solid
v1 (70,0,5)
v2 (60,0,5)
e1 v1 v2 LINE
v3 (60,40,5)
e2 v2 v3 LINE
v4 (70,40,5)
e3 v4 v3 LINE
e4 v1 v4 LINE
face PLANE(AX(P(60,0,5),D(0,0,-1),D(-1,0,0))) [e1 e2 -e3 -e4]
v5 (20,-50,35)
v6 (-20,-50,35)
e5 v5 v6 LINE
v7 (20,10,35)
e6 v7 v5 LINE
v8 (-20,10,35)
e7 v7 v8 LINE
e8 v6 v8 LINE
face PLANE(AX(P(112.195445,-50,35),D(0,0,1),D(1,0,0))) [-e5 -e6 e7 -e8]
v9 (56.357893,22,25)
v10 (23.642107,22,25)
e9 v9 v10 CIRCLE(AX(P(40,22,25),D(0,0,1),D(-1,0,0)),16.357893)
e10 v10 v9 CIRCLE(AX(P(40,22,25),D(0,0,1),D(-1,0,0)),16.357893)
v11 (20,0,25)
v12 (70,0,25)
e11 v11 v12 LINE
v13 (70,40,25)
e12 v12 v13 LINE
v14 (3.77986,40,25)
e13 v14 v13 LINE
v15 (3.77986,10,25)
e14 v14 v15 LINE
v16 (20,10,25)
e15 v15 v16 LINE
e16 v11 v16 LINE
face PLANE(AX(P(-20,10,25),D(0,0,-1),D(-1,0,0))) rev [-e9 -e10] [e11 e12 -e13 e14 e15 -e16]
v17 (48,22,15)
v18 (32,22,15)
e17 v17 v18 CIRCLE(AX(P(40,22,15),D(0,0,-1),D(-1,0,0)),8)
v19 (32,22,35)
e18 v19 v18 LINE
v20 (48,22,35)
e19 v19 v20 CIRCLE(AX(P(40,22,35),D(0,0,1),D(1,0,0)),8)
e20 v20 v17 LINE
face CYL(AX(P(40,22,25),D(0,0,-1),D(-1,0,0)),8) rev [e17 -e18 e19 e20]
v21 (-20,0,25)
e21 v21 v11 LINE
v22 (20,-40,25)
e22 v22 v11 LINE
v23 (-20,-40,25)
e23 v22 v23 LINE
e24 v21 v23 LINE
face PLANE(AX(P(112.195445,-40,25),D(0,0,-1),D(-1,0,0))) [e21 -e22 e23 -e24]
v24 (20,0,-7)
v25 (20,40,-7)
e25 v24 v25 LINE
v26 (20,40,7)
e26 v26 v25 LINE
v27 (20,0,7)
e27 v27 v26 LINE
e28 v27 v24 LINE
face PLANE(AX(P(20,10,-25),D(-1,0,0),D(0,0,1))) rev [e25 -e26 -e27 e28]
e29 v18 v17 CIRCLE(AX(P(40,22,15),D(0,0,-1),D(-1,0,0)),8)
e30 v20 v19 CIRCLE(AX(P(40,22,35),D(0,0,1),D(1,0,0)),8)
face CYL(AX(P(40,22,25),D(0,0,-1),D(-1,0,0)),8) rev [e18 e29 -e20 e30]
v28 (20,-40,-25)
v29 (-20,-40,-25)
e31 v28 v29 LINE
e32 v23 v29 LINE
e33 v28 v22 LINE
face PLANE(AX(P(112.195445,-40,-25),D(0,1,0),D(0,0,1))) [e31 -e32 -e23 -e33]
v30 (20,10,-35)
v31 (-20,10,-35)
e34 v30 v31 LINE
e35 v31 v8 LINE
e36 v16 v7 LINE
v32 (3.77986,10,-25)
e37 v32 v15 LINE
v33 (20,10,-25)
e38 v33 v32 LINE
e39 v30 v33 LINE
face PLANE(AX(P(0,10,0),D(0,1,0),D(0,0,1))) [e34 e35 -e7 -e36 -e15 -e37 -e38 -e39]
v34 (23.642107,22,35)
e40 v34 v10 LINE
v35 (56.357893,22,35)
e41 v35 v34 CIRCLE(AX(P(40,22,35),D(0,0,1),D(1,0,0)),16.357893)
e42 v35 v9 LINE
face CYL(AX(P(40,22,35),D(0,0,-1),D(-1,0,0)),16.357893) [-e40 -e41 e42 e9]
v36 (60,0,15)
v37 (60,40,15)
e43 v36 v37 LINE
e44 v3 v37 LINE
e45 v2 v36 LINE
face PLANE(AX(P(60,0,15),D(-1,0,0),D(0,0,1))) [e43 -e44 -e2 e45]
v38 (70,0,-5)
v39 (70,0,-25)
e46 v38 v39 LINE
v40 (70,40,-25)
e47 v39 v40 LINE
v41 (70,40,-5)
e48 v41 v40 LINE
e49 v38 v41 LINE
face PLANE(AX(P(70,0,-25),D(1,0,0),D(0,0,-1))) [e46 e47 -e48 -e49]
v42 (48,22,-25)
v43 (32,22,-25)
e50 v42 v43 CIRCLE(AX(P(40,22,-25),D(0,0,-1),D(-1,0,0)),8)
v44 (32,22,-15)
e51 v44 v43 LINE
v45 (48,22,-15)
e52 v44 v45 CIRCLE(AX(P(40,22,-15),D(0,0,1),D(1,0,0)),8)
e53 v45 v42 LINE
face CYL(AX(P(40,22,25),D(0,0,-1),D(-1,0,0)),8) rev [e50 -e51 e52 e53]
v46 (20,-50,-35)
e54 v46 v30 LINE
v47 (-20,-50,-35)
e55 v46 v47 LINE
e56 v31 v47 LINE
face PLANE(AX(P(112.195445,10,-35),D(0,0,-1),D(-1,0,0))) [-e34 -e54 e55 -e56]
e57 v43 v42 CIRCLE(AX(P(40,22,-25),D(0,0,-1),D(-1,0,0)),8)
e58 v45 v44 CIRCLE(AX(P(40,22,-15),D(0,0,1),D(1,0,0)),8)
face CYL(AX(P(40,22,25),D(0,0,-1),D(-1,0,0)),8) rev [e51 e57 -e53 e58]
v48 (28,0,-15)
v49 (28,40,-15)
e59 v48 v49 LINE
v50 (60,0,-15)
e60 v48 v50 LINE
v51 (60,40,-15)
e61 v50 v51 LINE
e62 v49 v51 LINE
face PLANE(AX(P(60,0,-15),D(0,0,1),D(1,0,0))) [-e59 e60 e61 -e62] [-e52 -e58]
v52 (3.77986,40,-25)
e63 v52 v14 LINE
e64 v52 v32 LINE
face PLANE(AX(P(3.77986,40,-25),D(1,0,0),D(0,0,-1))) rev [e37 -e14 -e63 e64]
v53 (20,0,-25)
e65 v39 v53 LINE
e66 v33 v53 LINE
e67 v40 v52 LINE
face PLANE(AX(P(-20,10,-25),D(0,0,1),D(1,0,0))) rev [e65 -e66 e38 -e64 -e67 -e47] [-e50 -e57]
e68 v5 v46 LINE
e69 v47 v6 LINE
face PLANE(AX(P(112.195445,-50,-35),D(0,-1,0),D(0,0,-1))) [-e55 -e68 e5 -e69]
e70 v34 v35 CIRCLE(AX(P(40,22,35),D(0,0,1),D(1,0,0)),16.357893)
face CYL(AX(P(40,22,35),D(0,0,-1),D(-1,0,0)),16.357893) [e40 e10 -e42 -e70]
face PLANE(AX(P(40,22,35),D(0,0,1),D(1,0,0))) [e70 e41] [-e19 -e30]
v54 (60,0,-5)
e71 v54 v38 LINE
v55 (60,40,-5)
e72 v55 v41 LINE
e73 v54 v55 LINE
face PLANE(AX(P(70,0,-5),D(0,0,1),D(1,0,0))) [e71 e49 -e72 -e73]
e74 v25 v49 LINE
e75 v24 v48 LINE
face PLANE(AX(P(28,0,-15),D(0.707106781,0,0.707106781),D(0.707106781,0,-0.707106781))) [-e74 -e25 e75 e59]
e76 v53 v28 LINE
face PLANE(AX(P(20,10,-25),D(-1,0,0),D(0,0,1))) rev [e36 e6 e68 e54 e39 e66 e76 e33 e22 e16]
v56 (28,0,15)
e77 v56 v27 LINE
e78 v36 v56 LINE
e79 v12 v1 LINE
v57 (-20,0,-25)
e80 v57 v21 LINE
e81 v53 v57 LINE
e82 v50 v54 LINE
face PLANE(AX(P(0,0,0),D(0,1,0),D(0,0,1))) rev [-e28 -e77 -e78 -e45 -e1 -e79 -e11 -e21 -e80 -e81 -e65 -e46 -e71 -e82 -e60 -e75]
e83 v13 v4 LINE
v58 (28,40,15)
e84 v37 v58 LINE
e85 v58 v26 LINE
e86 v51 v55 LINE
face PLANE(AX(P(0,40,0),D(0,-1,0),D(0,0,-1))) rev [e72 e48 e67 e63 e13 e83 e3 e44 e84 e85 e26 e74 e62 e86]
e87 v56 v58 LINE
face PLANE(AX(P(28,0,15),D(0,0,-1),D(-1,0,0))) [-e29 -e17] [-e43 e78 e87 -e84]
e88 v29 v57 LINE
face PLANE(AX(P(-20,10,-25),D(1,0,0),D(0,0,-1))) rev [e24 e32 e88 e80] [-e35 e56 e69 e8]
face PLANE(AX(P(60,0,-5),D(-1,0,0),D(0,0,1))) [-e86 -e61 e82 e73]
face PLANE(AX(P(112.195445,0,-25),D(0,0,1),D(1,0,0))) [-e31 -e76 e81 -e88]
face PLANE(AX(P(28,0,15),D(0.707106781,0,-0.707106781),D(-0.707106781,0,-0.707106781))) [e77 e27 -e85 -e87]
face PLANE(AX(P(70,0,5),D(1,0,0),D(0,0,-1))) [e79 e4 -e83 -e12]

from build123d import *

# Parameters (mm, degrees)
SKETCH1_W           = 40
SKETCH1_H           = 50
BOSS_EXTRUDE1_DEPTH = 10
BOSS_EXTRUDE2_DEPTH = 10
BOSS_EXTRUDE3_DEPTH = 40
BOSS_EXTRUDE4_DEPTH = 30
SKETCH5_R           = 8
CUT_EXTRUDE1_DEPTH  = 50
SKETCH6_R           = 16.35789331
SKETCH6_R_2         = 8
BOSS_EXTRUDE5_DEPTH = 10


with BuildPart() as part:
    # Sketch1 → Boss-Extrude1 (new body)
    with BuildSketch(Plane(origin=(0, 0, 0), x_dir=(1, 0, 0), z_dir=(0, 1, 0))):
        Rectangle(SKETCH1_W, SKETCH1_H)
    extrude(amount=BOSS_EXTRUDE1_DEPTH)

    # Sketch2 → Boss-Extrude2 (add)
    with BuildSketch(Plane(origin=(0, 10, 0), x_dir=(1, 0, 0), z_dir=(0, 1, 0))):
        Polygon((28, -15), (60, -15), (60, -5), (70, -5), (70, -25), (20, -25), (20, -15), (20, -7), align=None)
        Polygon((20, 25), (70, 25), (70, 5), (60, 5), (60, 15), (28, 15), (20, 7), (20, 15), align=None)
    extrude(amount=-BOSS_EXTRUDE2_DEPTH)

    # Sketch3 → Boss-Extrude3 (add)
    with BuildSketch(Plane.ZY.offset(20)):
        Polygon((-25, 10), (-35, 10), (-35, -50), (35, -50), (35, 10), (25, 10), (25, 0), (25, -40), (-25, -40), (-25, 0), align=None)
    extrude(amount=-BOSS_EXTRUDE3_DEPTH)

    # Sketch4 → Boss-Extrude4 (add)
    with BuildSketch(Plane(origin=(0, 10, 0), x_dir=(1, 0, 0), z_dir=(0, 1, 0))):
        Polygon((20, 7), (28, 15), (60, 15), (60, 5), (70, 5), (70, 25), (3.779860002, 25), (3.779860002, -25), (70, -25), (70, -5), (60, -5), (60, -15), (28, -15), (20, -7), align=None)
    extrude(amount=BOSS_EXTRUDE4_DEPTH)

    # Sketch5 → Cut-Extrude1 (cut)
    with BuildSketch(Plane(origin=(0, 0, -25), x_dir=(-1, 0, 0), z_dir=(0, 0, -1))):
        with Locations((-40, 22)):
            Circle(SKETCH5_R)
    extrude(amount=-CUT_EXTRUDE1_DEPTH, mode=Mode.SUBTRACT)

    # Sketch6 → Boss-Extrude5 (add)
    with BuildSketch(Plane.XY.offset(25)):
        with Locations(Location((40, 22, 0), (0, 0, 180))):
            Circle(SKETCH6_R)
        with Locations(Location((40, 22, 0), (0, 0, 180))):
            Circle(SKETCH6_R_2, mode=Mode.SUBTRACT)
    extrude(amount=BOSS_EXTRUDE5_DEPTH)


solid = part.part
